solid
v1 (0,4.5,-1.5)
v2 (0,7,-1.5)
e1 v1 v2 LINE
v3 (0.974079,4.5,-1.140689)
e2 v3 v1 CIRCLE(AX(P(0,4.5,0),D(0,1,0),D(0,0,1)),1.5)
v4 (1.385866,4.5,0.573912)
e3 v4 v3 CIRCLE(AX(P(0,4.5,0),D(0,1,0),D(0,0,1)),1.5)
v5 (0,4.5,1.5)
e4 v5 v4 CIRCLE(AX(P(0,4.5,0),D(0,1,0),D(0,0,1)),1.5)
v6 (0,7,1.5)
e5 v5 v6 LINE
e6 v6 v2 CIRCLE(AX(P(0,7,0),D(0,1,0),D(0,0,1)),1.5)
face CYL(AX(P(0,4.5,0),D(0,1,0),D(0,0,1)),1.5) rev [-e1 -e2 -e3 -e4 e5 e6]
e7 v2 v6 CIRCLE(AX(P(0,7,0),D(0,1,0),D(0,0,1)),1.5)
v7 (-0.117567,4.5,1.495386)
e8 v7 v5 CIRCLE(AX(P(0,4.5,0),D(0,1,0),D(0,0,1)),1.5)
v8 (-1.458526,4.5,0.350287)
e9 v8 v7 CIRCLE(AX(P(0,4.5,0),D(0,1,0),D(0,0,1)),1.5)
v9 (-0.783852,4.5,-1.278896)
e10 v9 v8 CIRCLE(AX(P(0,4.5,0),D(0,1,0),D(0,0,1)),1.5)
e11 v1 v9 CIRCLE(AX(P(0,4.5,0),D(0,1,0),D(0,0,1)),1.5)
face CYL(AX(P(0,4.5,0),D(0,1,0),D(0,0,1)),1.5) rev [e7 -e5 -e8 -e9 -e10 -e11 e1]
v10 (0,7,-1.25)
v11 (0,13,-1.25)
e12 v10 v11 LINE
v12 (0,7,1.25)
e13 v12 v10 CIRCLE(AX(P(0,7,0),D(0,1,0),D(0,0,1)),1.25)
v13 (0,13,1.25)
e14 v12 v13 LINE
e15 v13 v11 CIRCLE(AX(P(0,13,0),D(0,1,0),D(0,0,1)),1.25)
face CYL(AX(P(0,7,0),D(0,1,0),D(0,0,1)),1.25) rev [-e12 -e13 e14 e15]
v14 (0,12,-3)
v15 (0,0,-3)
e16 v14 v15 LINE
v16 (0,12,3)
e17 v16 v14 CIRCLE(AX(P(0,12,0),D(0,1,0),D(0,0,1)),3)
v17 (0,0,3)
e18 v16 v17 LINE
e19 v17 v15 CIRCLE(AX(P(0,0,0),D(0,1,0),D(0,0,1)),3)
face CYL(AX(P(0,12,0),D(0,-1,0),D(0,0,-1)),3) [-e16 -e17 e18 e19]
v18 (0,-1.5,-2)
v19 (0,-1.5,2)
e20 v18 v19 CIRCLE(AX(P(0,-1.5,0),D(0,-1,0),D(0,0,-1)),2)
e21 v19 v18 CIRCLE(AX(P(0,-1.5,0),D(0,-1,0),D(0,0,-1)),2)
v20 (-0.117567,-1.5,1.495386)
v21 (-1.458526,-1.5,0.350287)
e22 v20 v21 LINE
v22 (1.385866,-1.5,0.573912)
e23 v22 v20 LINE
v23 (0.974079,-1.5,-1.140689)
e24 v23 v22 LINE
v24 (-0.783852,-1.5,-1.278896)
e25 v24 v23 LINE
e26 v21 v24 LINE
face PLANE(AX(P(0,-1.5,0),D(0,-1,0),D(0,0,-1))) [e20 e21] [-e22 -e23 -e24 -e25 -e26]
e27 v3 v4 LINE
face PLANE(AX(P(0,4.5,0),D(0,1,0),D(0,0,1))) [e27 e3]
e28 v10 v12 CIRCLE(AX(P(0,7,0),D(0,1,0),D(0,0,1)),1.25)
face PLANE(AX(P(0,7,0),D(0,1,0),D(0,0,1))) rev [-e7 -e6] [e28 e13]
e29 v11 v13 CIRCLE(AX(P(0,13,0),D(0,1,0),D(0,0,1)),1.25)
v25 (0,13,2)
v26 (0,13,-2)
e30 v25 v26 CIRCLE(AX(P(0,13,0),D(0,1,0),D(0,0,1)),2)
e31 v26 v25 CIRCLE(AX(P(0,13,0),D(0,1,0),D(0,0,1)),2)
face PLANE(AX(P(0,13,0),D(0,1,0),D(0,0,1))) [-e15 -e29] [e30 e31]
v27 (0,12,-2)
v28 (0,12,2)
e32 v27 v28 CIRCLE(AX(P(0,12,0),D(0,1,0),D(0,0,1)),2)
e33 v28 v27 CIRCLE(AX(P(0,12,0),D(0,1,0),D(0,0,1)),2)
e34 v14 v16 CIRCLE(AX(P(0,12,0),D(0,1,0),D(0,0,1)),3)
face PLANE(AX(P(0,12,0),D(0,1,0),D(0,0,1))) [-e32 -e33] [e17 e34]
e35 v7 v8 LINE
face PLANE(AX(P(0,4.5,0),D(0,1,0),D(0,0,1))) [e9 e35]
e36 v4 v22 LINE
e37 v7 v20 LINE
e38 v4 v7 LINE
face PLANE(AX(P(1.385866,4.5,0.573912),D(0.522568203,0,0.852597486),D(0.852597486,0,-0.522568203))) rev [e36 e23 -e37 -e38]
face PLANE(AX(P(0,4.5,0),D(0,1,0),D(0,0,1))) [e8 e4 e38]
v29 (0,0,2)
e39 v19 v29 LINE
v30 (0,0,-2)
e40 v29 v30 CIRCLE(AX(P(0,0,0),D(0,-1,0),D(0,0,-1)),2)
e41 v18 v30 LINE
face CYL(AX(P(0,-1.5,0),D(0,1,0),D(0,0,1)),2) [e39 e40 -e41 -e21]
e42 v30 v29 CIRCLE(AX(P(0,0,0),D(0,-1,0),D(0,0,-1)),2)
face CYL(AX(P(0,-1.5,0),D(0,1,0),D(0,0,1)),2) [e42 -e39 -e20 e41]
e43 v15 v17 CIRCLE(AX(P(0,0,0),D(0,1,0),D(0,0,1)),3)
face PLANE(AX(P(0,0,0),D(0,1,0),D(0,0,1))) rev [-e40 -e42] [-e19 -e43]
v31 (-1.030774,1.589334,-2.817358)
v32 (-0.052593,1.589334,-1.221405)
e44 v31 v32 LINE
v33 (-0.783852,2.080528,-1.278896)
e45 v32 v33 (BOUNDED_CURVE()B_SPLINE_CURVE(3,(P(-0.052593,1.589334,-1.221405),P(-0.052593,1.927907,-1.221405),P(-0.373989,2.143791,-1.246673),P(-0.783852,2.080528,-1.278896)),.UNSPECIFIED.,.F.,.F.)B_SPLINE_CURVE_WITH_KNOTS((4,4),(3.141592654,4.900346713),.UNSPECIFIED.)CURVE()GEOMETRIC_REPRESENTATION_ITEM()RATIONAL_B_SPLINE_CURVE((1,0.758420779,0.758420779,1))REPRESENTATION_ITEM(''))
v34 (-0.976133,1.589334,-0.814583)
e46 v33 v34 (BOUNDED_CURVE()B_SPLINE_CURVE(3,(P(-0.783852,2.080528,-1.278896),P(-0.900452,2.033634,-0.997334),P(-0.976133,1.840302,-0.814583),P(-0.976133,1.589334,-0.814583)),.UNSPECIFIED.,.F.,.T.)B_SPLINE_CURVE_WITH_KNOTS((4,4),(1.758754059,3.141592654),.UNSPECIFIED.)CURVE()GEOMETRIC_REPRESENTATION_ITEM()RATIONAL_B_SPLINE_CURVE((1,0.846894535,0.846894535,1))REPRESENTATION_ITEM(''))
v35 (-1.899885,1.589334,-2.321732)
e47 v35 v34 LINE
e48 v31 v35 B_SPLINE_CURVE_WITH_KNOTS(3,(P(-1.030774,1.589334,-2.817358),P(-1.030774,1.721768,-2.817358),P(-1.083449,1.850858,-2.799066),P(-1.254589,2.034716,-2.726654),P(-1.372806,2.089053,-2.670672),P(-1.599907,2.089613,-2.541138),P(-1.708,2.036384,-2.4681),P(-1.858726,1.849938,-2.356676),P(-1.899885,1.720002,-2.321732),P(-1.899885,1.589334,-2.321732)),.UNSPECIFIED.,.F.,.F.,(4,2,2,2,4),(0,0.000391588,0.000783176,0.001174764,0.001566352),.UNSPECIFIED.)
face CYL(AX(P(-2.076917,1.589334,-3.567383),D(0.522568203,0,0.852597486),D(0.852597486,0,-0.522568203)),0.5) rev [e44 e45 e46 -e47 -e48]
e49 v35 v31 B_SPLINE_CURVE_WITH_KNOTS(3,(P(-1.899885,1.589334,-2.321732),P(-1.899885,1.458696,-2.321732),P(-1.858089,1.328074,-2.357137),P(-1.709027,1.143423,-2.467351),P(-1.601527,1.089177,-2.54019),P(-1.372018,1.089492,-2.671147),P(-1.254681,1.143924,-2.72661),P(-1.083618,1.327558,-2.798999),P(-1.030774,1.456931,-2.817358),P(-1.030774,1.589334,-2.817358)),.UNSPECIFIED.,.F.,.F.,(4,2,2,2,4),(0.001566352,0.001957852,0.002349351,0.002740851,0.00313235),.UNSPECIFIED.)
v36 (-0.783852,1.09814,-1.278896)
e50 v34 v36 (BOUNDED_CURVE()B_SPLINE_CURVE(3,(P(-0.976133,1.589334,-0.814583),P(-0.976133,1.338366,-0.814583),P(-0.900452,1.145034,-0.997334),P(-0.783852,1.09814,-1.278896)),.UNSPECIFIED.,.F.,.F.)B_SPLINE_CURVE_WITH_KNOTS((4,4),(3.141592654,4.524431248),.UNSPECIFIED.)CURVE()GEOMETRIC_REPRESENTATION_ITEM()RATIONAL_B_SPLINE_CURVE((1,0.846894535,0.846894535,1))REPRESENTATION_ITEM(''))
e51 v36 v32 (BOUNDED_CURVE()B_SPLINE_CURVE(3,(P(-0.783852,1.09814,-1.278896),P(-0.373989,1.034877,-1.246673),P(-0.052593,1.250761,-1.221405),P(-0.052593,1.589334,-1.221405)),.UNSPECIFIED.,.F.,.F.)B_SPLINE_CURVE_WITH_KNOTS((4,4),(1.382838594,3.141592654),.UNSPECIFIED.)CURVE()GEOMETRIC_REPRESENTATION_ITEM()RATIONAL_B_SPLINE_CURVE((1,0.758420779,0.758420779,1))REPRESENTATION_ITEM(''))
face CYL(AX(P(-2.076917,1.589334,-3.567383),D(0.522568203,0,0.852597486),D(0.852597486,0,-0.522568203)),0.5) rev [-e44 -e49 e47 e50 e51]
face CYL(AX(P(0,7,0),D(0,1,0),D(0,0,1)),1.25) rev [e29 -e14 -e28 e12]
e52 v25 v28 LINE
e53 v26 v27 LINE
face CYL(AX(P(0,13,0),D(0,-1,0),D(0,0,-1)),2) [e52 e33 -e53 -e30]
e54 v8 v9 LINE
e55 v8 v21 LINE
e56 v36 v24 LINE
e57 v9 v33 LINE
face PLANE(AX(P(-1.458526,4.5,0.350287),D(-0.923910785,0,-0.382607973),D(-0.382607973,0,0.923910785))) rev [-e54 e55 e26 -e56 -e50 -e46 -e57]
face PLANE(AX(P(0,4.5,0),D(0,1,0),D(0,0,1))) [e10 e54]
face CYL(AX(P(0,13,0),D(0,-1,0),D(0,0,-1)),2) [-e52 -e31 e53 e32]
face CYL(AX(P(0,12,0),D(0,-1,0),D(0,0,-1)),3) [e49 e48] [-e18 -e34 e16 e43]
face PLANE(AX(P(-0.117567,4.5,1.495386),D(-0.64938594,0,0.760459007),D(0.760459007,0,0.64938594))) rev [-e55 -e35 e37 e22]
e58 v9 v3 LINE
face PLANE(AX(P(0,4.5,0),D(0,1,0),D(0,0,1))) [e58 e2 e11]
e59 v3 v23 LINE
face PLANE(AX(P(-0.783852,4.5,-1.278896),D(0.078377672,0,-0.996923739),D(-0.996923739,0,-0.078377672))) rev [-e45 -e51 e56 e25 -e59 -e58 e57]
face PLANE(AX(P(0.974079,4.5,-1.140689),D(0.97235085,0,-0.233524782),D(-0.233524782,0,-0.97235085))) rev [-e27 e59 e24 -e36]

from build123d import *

# Parameters (mm, degrees)
SKETCH_2_R           = 3
BOSS_EXTRUDE_1_DEPTH = 12
SKETCH_3_R           = 2
BOSS_EXTRUDE_2_DEPTH = 1
BOSS_EXTRUDE_START   = 1.5
SKETCH_4_R           = 2
BOSS_EXTRUDE_3_DEPTH = 1.5
SKETCH_5_R           = 1.25
CUT_EXTRUDE_1_DEPTH  = 6
SKETCH_6_R           = 1.5
CUT_EXTRUDE_2_DEPTH  = 2.5
CUT_EXTRUDE_3_DEPTH  = 6
CUT_EXTRUDE_START    = -0.43115
SKETCH_11_R          = 0.5
CUT_EXTRUDE_8_DEPTH  = 1.93115


with BuildPart() as part:
    # Sketch 2 → Boss-Extrude 1 (new body)
    with BuildSketch(Plane(origin=(0, 0, 0), x_dir=(1, 0, 0), z_dir=(0, 1, 0))):
        with Locations(Location((0, 0, 0), (0, 0, 270))):
            Circle(SKETCH_2_R)
    extrude(amount=BOSS_EXTRUDE_1_DEPTH)

    # Sketch 3 → Boss-Extrude 2 (add)
    with BuildSketch(Plane(origin=(0, 12, 0), x_dir=(1, 0, 0), z_dir=(0, 1, 0))):
        with Locations(Location((0, 0, 0), (0, 0, 270))):
            Circle(SKETCH_3_R)
    extrude(amount=BOSS_EXTRUDE_2_DEPTH)

    # Sketch 4 → Boss-Extrude 3 (add)
    with BuildSketch(Plane(origin=(0, 0, 0), x_dir=(-1, 0, 0), z_dir=(0, -1, 0)).offset(BOSS_EXTRUDE_START)):
        with Locations(Location((0, 0, 0), (0, 0, 270))):
            Circle(SKETCH_4_R)
    extrude(amount=-BOSS_EXTRUDE_3_DEPTH)

    # Sketch 5 → Cut-Extrude 1 (cut)
    with BuildSketch(Plane(origin=(0, 13, 0), x_dir=(1, 0, 0), z_dir=(0, 1, 0))):
        with Locations(Location((0, 0, 0), (0, 0, 270))):
            Circle(SKETCH_5_R)
    extrude(amount=-CUT_EXTRUDE_1_DEPTH, mode=Mode.SUBTRACT)

    # Sketch 6 → Cut-Extrude 2 (cut)
    with BuildSketch(Plane(origin=(0, 7, 0), x_dir=(1, 0, 0), z_dir=(0, 1, 0))):
        with Locations(Location((0, 0, 0), (0, 0, 270))):
            Circle(SKETCH_6_R)
    extrude(amount=-CUT_EXTRUDE_2_DEPTH, mode=Mode.SUBTRACT)

    # Sketch 7 → Cut-Extrude 3 (cut)
    with BuildSketch(Plane(origin=(0, -1.5, 0), x_dir=(-1, 0, 0), z_dir=(0, -1, 0))):
        Polygon((-0.97407891, 1.14068851), (-1.385866178, -0.57391196), (0.117566508, -1.495385608), (1.458526276, -0.350287172), (0.783852304, 1.27889623), align=None)
    extrude(amount=-CUT_EXTRUDE_3_DEPTH, mode=Mode.SUBTRACT)

    # Sketch 11 → Cut-Extrude 8 (cut)
    with BuildSketch(Plane(origin=(-0.783852304, 0, -1.27889623), x_dir=(-0.8525974863360001, 0, 0.5225682025281811), z_dir=(-0.5225682025281811, 0, -0.8525974863360001)).offset(CUT_EXTRUDE_START)):
        with Locations(Location((-0.093426493, 1.5893341, 0), (0, 0, 180))):
            Circle(SKETCH_11_R)
    extrude(amount=CUT_EXTRUDE_8_DEPTH, mode=Mode.SUBTRACT)


solid = part.part
